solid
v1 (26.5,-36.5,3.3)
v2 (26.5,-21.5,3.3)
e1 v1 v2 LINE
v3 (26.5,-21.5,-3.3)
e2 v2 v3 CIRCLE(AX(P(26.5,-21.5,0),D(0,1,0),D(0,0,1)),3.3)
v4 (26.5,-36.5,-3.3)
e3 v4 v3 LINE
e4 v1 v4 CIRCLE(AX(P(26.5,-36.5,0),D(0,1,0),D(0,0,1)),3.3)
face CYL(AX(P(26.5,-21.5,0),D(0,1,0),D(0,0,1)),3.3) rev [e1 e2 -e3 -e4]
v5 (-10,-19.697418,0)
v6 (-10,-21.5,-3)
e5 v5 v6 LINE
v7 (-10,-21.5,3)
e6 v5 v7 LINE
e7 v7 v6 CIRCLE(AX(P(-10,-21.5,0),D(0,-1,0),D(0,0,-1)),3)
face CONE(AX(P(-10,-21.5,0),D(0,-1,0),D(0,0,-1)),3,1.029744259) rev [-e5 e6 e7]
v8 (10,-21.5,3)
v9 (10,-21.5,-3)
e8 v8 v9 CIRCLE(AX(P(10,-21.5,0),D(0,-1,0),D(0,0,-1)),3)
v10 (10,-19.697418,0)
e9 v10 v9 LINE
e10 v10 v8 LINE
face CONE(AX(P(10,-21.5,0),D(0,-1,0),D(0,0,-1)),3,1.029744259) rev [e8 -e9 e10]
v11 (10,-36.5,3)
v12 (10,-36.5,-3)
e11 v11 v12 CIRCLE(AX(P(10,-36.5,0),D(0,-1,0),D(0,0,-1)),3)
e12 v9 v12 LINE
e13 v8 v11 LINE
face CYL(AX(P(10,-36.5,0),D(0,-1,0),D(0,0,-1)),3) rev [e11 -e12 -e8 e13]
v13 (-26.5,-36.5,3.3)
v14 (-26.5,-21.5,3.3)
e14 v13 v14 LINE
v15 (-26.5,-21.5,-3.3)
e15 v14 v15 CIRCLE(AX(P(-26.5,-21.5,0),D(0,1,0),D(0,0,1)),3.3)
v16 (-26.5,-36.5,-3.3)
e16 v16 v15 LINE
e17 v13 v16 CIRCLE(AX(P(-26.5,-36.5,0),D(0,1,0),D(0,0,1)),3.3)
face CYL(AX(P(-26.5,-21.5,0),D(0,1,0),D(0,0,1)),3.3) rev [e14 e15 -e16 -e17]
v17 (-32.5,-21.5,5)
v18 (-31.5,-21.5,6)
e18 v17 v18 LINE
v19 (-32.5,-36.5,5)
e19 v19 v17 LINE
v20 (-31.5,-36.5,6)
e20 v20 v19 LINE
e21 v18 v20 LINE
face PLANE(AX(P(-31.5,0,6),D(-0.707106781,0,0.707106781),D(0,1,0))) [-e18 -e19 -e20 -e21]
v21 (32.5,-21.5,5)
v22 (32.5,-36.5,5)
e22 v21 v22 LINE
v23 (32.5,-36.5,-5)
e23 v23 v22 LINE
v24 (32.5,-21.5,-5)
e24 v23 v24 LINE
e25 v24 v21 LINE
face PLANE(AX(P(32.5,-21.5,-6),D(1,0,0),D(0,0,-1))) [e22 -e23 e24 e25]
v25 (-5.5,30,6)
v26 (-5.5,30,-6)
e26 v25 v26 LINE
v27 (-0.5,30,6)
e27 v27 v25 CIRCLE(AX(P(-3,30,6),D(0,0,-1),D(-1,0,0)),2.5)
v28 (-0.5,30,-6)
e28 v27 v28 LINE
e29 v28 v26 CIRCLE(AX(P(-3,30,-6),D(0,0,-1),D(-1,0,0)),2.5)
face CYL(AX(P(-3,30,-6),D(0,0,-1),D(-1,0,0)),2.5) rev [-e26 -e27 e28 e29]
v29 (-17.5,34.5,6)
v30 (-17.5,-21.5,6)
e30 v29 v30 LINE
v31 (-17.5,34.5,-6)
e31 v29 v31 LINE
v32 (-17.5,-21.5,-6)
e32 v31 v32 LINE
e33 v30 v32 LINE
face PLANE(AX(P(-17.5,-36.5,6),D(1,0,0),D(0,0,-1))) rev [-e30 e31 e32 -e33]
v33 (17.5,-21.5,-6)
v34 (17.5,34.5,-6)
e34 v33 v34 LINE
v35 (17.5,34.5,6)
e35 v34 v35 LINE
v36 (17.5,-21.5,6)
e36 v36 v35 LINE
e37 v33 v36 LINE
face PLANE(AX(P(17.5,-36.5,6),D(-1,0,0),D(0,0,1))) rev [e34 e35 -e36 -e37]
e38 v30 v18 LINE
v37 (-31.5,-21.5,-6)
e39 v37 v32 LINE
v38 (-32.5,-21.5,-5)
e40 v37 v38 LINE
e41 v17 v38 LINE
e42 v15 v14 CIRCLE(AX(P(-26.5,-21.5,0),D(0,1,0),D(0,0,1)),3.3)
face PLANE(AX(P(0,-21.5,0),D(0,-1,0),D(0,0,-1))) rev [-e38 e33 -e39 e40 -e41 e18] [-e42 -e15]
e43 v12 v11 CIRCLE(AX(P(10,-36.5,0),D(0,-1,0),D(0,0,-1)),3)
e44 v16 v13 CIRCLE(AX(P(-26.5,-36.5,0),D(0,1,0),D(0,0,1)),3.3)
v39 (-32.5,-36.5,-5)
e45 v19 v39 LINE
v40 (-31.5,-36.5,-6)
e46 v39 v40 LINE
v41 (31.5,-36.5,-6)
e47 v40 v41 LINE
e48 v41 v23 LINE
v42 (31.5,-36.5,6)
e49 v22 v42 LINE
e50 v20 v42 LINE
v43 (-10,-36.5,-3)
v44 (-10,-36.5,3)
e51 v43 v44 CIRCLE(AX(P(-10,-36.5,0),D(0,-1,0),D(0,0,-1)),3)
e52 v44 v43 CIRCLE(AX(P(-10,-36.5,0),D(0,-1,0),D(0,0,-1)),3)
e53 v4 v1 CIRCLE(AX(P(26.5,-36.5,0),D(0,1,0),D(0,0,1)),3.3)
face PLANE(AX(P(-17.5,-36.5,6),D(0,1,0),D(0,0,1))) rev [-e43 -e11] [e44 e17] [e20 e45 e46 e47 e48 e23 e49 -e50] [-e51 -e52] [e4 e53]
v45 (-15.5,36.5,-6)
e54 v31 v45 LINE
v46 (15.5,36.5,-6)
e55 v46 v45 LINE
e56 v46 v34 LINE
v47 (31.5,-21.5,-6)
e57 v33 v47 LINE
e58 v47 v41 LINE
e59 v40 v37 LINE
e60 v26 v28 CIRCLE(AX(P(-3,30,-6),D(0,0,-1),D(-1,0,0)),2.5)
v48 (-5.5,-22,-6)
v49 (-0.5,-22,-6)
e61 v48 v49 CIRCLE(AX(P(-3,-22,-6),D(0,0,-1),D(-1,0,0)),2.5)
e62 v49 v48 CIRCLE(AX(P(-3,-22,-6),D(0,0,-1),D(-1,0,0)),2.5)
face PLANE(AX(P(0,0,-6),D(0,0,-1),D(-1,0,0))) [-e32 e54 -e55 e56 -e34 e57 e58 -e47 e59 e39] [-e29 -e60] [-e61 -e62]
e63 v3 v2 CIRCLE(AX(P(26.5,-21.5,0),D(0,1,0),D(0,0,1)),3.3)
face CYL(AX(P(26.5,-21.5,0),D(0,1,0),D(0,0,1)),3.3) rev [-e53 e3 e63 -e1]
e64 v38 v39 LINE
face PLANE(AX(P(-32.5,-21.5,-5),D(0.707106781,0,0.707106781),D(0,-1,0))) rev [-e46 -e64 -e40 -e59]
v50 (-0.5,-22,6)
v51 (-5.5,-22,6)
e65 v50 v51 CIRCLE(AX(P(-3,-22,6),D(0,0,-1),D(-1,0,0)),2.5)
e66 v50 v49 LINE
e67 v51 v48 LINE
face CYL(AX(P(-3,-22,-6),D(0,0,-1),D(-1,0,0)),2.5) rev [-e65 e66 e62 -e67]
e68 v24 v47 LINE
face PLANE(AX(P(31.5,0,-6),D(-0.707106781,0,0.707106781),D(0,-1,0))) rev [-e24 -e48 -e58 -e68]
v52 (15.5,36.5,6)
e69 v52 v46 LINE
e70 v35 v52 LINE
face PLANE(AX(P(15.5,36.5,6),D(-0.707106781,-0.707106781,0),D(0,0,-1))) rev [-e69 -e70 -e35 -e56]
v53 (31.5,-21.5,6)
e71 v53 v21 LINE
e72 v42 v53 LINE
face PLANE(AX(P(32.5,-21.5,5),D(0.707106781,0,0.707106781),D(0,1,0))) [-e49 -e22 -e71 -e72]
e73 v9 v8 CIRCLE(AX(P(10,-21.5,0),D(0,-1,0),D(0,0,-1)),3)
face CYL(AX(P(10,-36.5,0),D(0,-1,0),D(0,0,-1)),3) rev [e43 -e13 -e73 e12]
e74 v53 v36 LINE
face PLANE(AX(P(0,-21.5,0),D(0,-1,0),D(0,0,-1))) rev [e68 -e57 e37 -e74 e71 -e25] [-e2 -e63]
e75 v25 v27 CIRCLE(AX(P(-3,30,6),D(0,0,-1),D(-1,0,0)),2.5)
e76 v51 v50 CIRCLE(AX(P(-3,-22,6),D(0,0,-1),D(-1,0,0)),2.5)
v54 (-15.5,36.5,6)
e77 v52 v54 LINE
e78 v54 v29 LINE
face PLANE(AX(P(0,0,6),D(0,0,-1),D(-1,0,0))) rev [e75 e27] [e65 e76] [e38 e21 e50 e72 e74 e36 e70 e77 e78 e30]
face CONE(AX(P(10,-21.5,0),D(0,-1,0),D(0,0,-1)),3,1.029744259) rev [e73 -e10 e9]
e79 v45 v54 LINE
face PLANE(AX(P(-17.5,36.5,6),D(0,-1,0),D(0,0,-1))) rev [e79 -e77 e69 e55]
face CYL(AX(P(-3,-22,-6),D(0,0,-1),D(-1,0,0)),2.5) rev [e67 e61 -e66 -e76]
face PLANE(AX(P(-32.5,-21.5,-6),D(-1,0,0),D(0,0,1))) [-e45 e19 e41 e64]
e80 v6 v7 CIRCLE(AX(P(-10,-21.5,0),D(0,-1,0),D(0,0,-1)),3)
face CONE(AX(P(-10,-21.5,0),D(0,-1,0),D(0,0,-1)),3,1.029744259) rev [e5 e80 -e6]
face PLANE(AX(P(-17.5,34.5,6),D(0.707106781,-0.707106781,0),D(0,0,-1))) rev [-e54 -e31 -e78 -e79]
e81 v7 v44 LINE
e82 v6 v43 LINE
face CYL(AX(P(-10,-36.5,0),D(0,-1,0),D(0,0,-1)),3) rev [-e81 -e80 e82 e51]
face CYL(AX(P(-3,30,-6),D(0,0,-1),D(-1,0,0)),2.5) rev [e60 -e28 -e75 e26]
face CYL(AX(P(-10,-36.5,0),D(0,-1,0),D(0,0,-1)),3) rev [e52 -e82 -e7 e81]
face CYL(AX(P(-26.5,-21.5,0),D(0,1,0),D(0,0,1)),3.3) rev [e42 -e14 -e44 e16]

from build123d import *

# Parameters (mm, degrees)
SKETCH_1_W           = 35
SKETCH_1_H           = 73
EXTRUDE_1_DEPTH      = 6
SKETCH_2_W           = 65
SKETCH_2_H           = 12
EXTRUDE_2_DEPTH      = 15
HOLE_WIZARD_M6_1_D   = 6.6
F_6_0MM_1_D          = 6
F_6_0MM_1_DEPTH      = 15
F_6_0MM_1_TIP        = 1.802581857
HOLE_WIZARD_M6_1_2_D = 5
CHAMFER_1_SIZE       = 1
CHAMFER_2_SIZE       = 2


with BuildPart() as part:
    # 草图1 → 凸台-拉伸1 (new, symmetric)
    with BuildSketch(Plane.XY):
        Rectangle(SKETCH_1_W, SKETCH_1_H)
    extrude(amount=EXTRUDE_1_DEPTH, both=True)

    # 草图2 → 凸台-拉伸2 (add)
    with BuildSketch(Plane.XZ.offset(36.5)):
        Rectangle(SKETCH_2_W, SKETCH_2_H)
    extrude(amount=-EXTRUDE_2_DEPTH)

    # Hole Wizard M6 _1 (through all)
    with Locations(Plane(origin=(0, -21.5, 0), x_dir=(1, 0, 0), z_dir=(0, 1, 0))):
        with Locations((-26.5, 0), (26.5, 0)):
            Hole(HOLE_WIZARD_M6_1_D / 2)

    # Ø6.0mm 暗销孔1
    with Locations(Plane(origin=(0, -36.5, 0), x_dir=(-1, 0, 0), z_dir=(0, -1, 0))):
        with Locations((10, 0), (-10, 0)):
            Hole(F_6_0MM_1_D / 2, depth=F_6_0MM_1_DEPTH)
            with Locations((0, 0, -(F_6_0MM_1_DEPTH + F_6_0MM_1_TIP / 2))):  # 118° drill point
                Cone(0, F_6_0MM_1_D / 2, F_6_0MM_1_TIP, mode=Mode.SUBTRACT)

    # Hole Wizard M6 _1 2 (through all)
    with Locations(Plane(origin=(0, 0, -6), x_dir=(-1, 0, 0), z_dir=(0, 0, -1))):
        with Locations((3, -22), (3, 30)):
            Hole(HOLE_WIZARD_M6_1_2_D / 2)

    # 倒角1
    chamfer_1_edges = [part.edges().sort_by_distance(p)[0] for p in [
        (-32.5, -29, 6),
        (32.5, -29, -6),
        (-32.5, -29, -6),
        (32.5, -29, 6),
    ]]
    chamfer(chamfer_1_edges, length=CHAMFER_1_SIZE)

    # 倒角2
    chamfer_2_edges = [part.edges().sort_by_distance(p)[0] for p in [
        (-17.5, 36.5, 0),
        (17.5, 36.5, 0),
    ]]
    chamfer(chamfer_2_edges, length=CHAMFER_2_SIZE)


solid = part.part
